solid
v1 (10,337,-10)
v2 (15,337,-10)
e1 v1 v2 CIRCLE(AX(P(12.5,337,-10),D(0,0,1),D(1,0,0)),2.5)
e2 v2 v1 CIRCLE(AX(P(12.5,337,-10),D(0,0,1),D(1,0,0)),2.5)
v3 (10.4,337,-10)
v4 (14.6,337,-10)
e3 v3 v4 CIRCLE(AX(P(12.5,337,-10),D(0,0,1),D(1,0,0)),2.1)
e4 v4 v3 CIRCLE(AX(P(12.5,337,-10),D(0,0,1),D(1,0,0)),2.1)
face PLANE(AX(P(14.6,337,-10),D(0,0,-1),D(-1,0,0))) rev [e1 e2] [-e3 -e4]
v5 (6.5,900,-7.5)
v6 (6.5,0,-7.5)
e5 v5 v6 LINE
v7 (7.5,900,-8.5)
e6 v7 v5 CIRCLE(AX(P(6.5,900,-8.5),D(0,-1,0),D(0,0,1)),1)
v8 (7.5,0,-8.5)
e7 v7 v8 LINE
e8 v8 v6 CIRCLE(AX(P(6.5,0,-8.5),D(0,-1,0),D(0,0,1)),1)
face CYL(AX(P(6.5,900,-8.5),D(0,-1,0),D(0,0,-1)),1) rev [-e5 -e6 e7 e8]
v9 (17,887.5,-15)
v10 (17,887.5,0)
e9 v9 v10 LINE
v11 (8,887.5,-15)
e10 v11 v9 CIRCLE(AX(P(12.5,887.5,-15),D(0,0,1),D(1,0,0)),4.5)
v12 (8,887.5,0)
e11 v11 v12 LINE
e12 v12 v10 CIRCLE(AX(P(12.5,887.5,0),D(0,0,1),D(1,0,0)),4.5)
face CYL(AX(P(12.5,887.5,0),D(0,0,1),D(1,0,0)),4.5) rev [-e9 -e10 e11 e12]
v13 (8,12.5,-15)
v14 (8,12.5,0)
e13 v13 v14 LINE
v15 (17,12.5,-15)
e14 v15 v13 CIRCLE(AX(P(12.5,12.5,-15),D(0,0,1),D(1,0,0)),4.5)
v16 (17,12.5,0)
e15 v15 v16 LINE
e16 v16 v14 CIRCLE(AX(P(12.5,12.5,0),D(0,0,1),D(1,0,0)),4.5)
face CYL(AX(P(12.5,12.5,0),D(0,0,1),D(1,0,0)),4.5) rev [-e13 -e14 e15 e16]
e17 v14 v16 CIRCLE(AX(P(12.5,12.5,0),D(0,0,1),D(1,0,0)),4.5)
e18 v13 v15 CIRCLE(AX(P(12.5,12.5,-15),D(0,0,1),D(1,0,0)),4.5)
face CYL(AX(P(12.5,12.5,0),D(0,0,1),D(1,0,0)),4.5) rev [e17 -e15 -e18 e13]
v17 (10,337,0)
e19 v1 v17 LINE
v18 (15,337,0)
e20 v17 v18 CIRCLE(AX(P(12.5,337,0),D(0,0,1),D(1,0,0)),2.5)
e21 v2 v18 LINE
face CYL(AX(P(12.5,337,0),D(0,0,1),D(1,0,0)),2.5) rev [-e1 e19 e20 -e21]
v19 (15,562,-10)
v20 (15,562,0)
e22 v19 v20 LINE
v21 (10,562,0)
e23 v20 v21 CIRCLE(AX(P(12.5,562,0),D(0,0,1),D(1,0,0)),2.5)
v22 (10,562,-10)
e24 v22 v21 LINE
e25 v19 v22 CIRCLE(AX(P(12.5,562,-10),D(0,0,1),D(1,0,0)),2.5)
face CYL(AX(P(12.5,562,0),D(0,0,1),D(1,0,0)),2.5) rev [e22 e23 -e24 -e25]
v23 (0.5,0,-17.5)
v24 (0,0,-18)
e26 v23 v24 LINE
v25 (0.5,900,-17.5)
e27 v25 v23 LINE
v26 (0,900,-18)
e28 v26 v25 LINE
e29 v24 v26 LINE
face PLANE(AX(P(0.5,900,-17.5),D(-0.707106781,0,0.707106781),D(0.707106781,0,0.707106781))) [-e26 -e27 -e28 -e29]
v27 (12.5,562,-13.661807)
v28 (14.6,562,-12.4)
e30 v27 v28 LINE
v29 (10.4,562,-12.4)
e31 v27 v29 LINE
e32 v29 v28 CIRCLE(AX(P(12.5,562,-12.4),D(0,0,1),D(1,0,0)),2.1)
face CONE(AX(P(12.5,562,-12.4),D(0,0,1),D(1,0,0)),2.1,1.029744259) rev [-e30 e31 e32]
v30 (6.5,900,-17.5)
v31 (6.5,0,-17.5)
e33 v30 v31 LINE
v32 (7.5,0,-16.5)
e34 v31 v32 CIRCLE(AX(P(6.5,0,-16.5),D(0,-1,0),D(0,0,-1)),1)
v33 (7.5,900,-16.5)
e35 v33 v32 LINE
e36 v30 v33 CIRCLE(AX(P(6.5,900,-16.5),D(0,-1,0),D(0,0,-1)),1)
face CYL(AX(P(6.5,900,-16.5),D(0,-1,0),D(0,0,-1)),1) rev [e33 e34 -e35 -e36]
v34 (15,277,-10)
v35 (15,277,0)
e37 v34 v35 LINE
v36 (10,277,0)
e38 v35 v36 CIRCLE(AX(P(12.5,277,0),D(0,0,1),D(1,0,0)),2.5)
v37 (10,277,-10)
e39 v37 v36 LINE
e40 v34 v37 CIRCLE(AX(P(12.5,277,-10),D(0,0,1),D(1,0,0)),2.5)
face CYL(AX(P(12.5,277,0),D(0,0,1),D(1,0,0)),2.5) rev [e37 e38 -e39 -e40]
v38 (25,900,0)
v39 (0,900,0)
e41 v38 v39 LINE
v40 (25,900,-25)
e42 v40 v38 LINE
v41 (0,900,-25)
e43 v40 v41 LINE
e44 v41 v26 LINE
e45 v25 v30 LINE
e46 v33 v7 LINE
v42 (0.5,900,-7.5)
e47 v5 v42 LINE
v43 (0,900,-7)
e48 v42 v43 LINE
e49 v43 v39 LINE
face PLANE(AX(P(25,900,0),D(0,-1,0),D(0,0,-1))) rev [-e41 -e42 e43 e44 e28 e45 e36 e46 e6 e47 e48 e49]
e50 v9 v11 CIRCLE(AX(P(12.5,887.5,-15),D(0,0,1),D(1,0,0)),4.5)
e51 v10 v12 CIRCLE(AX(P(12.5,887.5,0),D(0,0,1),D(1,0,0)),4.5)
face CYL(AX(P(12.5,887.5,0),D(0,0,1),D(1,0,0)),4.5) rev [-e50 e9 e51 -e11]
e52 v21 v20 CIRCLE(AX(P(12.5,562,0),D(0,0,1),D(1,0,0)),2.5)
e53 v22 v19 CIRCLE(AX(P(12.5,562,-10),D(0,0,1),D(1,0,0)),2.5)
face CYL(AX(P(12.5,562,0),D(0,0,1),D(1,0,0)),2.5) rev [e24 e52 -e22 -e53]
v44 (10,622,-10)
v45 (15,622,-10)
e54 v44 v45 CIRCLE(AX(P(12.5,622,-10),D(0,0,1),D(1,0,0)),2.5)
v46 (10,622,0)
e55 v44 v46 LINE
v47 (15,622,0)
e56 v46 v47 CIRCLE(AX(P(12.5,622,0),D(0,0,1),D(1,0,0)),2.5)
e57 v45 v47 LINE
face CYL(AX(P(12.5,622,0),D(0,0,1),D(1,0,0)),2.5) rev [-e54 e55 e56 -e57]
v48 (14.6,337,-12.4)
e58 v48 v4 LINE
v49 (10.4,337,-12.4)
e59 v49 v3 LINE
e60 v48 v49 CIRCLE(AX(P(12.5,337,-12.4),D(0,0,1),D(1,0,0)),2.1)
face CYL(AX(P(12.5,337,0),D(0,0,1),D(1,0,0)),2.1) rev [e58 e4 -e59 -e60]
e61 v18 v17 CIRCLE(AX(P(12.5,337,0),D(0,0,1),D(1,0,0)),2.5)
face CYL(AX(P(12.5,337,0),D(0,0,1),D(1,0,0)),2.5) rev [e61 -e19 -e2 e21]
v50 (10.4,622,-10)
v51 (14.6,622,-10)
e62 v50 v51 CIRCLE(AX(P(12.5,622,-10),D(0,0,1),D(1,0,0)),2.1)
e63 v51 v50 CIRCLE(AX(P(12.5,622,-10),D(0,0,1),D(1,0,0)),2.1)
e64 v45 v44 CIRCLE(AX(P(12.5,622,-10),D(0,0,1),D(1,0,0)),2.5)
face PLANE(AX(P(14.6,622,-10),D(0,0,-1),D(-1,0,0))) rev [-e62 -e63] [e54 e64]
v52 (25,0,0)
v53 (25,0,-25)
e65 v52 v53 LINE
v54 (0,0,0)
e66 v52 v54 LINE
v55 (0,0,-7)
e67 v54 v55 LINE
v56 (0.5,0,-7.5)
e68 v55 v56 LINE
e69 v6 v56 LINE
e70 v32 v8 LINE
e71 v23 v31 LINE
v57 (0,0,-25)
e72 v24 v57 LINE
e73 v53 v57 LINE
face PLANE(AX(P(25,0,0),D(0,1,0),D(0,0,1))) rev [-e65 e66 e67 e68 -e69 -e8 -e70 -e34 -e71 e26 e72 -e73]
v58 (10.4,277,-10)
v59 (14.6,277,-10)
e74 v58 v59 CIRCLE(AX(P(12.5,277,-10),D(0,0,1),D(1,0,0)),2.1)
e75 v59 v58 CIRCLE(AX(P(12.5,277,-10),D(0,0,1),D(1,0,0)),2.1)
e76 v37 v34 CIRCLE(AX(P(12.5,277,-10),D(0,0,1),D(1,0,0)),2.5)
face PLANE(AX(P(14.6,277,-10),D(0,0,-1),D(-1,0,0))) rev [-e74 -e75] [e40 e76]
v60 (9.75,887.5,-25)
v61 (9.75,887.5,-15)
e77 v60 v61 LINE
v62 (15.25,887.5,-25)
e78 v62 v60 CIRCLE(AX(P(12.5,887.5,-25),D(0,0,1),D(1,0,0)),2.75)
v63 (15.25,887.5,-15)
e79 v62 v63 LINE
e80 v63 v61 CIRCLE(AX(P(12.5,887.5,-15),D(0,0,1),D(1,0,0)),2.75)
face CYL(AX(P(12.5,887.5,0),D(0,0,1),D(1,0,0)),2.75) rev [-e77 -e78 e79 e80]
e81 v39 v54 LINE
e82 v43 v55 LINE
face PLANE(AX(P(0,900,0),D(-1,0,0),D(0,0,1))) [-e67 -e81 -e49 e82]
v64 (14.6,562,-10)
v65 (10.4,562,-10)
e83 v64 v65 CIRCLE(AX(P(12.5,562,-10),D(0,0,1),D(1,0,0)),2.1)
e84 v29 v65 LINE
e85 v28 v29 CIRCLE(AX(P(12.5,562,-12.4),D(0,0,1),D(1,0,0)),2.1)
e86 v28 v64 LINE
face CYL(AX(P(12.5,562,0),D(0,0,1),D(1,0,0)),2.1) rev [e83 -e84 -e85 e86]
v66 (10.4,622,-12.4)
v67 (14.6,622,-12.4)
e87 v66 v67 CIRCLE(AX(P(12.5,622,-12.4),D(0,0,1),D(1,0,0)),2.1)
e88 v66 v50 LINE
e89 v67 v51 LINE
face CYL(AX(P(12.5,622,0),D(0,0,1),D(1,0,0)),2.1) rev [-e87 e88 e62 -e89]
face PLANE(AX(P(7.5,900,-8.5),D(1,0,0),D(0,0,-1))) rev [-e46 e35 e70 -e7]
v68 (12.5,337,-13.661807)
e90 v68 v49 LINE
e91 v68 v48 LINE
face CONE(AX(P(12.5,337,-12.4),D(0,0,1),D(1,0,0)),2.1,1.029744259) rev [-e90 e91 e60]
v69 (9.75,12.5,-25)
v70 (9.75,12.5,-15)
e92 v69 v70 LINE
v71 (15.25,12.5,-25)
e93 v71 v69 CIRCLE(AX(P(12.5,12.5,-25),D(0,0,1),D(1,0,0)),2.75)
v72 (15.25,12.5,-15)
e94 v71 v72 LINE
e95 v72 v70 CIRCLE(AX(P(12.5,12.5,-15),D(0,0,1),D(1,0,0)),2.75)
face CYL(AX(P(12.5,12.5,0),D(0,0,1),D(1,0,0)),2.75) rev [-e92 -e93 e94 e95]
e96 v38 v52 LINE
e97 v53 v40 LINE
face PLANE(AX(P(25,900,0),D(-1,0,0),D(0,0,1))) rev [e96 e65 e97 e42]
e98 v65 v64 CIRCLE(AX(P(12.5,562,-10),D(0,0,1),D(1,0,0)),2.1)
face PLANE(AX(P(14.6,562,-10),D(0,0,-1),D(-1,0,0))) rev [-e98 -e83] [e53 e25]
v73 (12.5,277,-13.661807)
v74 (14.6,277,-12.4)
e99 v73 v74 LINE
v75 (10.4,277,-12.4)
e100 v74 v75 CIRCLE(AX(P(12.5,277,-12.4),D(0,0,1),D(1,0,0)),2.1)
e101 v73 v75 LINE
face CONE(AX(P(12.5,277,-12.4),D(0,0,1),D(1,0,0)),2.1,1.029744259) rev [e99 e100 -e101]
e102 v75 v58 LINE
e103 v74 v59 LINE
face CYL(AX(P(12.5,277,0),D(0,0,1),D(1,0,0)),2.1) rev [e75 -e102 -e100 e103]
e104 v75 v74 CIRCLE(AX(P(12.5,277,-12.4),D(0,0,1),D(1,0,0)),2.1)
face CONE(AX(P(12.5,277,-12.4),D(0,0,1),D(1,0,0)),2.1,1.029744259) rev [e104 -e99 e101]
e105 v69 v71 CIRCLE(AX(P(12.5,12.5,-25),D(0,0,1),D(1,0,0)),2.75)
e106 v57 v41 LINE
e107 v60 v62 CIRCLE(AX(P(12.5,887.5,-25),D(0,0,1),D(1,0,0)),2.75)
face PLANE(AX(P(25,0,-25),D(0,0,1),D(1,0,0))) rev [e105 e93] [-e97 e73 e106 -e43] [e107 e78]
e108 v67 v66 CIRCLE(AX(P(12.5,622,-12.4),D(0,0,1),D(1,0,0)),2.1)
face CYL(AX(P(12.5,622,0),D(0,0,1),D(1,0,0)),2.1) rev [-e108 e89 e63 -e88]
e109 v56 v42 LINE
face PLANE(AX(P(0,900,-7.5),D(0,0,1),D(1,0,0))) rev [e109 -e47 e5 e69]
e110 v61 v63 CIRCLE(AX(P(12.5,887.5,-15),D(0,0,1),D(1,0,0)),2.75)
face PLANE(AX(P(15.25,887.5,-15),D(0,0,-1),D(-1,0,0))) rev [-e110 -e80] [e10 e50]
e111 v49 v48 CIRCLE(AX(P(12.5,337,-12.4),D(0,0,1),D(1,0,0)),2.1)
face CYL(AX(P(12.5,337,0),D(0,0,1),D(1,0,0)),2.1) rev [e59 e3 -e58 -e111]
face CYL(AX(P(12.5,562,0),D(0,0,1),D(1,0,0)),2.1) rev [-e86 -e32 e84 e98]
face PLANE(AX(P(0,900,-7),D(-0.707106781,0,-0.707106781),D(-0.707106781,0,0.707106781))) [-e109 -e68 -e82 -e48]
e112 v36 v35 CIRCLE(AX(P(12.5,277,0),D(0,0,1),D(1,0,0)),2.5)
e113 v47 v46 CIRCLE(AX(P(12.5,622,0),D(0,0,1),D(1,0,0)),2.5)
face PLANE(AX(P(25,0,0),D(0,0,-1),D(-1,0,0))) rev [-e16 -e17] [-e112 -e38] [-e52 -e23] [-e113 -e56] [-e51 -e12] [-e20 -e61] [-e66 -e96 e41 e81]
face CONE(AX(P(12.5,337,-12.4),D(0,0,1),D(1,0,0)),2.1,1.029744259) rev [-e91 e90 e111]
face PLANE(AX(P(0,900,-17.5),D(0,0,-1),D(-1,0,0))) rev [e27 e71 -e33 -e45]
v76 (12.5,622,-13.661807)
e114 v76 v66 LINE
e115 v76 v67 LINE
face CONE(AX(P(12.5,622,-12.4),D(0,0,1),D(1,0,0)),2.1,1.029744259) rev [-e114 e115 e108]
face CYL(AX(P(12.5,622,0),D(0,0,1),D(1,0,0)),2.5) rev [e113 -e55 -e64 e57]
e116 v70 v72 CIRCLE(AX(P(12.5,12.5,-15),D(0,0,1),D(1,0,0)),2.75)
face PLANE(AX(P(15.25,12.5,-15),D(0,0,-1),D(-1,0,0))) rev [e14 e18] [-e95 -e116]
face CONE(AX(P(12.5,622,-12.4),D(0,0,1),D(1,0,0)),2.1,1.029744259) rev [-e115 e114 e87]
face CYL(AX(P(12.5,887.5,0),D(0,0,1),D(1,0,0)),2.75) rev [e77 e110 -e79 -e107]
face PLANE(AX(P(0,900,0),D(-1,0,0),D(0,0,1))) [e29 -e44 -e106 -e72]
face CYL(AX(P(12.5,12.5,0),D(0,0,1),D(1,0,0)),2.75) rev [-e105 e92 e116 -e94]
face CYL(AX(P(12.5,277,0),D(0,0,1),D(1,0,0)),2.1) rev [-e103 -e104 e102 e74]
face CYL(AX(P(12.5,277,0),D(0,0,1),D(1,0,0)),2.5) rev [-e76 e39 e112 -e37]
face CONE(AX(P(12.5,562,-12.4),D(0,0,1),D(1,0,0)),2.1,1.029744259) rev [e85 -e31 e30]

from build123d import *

# Parameters (mm, degrees)
SKETCH_1_W                  = 25
SKETCH_1_H                  = 900
EXTRUDE_1_DEPTH             = 25
CUT_EXTRUDE_1_DEPTH         = 901.694176733
CHAMFER_1_SIZE              = 0.5
HOLE_WIZARD_1_D             = 5.5
HOLE_WIZARD_1_CBORE_D       = 9
HOLE_WIZARD_1_CBORE_DEPTH   = 15
HOLE_WIZARD_M5_1_AT_2_COUNT = 2
HOLE_WIZARD_M5_1_AT_2_PITCH = 60
PATTERN_LINEAR_1_COUNT      = 2
PATTERN_LINEAR_1_PITCH      = 285


with BuildPart() as part:
    # 草图1 → 拉伸1 (new body)
    with BuildSketch(Plane(origin=(0, 0, 0), x_dir=(0, 0, -1), z_dir=(1, 0, 0))):
        with Locations((12.5, 450)):
            Rectangle(SKETCH_1_W, SKETCH_1_H)
    extrude(amount=EXTRUDE_1_DEPTH)

    # 草图2 → 切除-拉伸1 (cut, through all)
    with BuildSketch(Plane.XZ):
        with BuildLine():
            Line((0, -7.5), (6.5, -7.5))
            ThreePointArc((6.5, -7.5), (7.207106781, -7.792893219), (7.5, -8.5))
            Line((7.5, -8.5), (7.5, -16.5))
            ThreePointArc((7.5, -16.5), (7.207106781, -17.207106781), (6.5, -17.5))
            Line((6.5, -17.5), (0, -17.5))
            Line((0, -17.5), (0, -7.5))
        make_face()
    extrude(amount=-CUT_EXTRUDE_1_DEPTH, mode=Mode.SUBTRACT)

    # 倒角1
    chamfer_1_edges = [part.edges().sort_by_distance(p)[0] for p in [
        (0, 450, -17.5),
        (0, 450, -7.5),
    ]]
    chamfer(chamfer_1_edges, length=CHAMFER_1_SIZE)

    # 孔1 (through all)
    with Locations(Plane(origin=(12.5, 887.5, 0), x_dir=(1, 0, 0), z_dir=(0, 0, 1))):
        with Locations((0, 0), (0, -875)):
            CounterBoreHole(HOLE_WIZARD_1_D / 2, HOLE_WIZARD_1_CBORE_D / 2, HOLE_WIZARD_1_CBORE_DEPTH)

    # 草图5 → M5 螺纹孔1 (revolve, cut)
    with BuildSketch(Plane(origin=(12.5, 622, 0), x_dir=(0, -1, 0), z_dir=(1, 0, 0))):
        Polygon((0, 0), (0, 13.6618073), (2.1, 12.4), (2.1, 10), (2.5, 10), (2.5, 0), align=None)
    hole_wizard_m5_1 = revolve(axis=Axis((12.5, 622, 6.35), (0, 0, -1)), mode=Mode.SUBTRACT)

    # M5 螺纹孔1 at 2: M5 螺纹孔1 ×2
    with Locations(*[(0, -i * HOLE_WIZARD_M5_1_AT_2_PITCH, 0) for i in range(1, HOLE_WIZARD_M5_1_AT_2_COUNT)]):
        add(hole_wizard_m5_1, mode=Mode.SUBTRACT)

    # 阵列(线性)1: M5 螺纹孔1 ×2
    with Locations(*[(0, -i * PATTERN_LINEAR_1_PITCH, 0) for i in range(1, PATTERN_LINEAR_1_COUNT)]):
        add(hole_wizard_m5_1, mode=Mode.SUBTRACT)

    # 阵列(线性)1 copy 1 sketch → 阵列(线性)1 copy 1 (revolve, cut)
    with BuildSketch(Plane(origin=(12.5, 277, 0), x_dir=(0, -1, 0), z_dir=(1, 0, 0))):
        Polygon((0, 0), (0, 13.6618073), (2.1, 12.4), (2.1, 10), (2.5, 10), (2.5, 0), align=None)
    revolve(axis=Axis((12.5, 277, 6.35), (0, 0, -1)), mode=Mode.SUBTRACT)


solid = part.part
